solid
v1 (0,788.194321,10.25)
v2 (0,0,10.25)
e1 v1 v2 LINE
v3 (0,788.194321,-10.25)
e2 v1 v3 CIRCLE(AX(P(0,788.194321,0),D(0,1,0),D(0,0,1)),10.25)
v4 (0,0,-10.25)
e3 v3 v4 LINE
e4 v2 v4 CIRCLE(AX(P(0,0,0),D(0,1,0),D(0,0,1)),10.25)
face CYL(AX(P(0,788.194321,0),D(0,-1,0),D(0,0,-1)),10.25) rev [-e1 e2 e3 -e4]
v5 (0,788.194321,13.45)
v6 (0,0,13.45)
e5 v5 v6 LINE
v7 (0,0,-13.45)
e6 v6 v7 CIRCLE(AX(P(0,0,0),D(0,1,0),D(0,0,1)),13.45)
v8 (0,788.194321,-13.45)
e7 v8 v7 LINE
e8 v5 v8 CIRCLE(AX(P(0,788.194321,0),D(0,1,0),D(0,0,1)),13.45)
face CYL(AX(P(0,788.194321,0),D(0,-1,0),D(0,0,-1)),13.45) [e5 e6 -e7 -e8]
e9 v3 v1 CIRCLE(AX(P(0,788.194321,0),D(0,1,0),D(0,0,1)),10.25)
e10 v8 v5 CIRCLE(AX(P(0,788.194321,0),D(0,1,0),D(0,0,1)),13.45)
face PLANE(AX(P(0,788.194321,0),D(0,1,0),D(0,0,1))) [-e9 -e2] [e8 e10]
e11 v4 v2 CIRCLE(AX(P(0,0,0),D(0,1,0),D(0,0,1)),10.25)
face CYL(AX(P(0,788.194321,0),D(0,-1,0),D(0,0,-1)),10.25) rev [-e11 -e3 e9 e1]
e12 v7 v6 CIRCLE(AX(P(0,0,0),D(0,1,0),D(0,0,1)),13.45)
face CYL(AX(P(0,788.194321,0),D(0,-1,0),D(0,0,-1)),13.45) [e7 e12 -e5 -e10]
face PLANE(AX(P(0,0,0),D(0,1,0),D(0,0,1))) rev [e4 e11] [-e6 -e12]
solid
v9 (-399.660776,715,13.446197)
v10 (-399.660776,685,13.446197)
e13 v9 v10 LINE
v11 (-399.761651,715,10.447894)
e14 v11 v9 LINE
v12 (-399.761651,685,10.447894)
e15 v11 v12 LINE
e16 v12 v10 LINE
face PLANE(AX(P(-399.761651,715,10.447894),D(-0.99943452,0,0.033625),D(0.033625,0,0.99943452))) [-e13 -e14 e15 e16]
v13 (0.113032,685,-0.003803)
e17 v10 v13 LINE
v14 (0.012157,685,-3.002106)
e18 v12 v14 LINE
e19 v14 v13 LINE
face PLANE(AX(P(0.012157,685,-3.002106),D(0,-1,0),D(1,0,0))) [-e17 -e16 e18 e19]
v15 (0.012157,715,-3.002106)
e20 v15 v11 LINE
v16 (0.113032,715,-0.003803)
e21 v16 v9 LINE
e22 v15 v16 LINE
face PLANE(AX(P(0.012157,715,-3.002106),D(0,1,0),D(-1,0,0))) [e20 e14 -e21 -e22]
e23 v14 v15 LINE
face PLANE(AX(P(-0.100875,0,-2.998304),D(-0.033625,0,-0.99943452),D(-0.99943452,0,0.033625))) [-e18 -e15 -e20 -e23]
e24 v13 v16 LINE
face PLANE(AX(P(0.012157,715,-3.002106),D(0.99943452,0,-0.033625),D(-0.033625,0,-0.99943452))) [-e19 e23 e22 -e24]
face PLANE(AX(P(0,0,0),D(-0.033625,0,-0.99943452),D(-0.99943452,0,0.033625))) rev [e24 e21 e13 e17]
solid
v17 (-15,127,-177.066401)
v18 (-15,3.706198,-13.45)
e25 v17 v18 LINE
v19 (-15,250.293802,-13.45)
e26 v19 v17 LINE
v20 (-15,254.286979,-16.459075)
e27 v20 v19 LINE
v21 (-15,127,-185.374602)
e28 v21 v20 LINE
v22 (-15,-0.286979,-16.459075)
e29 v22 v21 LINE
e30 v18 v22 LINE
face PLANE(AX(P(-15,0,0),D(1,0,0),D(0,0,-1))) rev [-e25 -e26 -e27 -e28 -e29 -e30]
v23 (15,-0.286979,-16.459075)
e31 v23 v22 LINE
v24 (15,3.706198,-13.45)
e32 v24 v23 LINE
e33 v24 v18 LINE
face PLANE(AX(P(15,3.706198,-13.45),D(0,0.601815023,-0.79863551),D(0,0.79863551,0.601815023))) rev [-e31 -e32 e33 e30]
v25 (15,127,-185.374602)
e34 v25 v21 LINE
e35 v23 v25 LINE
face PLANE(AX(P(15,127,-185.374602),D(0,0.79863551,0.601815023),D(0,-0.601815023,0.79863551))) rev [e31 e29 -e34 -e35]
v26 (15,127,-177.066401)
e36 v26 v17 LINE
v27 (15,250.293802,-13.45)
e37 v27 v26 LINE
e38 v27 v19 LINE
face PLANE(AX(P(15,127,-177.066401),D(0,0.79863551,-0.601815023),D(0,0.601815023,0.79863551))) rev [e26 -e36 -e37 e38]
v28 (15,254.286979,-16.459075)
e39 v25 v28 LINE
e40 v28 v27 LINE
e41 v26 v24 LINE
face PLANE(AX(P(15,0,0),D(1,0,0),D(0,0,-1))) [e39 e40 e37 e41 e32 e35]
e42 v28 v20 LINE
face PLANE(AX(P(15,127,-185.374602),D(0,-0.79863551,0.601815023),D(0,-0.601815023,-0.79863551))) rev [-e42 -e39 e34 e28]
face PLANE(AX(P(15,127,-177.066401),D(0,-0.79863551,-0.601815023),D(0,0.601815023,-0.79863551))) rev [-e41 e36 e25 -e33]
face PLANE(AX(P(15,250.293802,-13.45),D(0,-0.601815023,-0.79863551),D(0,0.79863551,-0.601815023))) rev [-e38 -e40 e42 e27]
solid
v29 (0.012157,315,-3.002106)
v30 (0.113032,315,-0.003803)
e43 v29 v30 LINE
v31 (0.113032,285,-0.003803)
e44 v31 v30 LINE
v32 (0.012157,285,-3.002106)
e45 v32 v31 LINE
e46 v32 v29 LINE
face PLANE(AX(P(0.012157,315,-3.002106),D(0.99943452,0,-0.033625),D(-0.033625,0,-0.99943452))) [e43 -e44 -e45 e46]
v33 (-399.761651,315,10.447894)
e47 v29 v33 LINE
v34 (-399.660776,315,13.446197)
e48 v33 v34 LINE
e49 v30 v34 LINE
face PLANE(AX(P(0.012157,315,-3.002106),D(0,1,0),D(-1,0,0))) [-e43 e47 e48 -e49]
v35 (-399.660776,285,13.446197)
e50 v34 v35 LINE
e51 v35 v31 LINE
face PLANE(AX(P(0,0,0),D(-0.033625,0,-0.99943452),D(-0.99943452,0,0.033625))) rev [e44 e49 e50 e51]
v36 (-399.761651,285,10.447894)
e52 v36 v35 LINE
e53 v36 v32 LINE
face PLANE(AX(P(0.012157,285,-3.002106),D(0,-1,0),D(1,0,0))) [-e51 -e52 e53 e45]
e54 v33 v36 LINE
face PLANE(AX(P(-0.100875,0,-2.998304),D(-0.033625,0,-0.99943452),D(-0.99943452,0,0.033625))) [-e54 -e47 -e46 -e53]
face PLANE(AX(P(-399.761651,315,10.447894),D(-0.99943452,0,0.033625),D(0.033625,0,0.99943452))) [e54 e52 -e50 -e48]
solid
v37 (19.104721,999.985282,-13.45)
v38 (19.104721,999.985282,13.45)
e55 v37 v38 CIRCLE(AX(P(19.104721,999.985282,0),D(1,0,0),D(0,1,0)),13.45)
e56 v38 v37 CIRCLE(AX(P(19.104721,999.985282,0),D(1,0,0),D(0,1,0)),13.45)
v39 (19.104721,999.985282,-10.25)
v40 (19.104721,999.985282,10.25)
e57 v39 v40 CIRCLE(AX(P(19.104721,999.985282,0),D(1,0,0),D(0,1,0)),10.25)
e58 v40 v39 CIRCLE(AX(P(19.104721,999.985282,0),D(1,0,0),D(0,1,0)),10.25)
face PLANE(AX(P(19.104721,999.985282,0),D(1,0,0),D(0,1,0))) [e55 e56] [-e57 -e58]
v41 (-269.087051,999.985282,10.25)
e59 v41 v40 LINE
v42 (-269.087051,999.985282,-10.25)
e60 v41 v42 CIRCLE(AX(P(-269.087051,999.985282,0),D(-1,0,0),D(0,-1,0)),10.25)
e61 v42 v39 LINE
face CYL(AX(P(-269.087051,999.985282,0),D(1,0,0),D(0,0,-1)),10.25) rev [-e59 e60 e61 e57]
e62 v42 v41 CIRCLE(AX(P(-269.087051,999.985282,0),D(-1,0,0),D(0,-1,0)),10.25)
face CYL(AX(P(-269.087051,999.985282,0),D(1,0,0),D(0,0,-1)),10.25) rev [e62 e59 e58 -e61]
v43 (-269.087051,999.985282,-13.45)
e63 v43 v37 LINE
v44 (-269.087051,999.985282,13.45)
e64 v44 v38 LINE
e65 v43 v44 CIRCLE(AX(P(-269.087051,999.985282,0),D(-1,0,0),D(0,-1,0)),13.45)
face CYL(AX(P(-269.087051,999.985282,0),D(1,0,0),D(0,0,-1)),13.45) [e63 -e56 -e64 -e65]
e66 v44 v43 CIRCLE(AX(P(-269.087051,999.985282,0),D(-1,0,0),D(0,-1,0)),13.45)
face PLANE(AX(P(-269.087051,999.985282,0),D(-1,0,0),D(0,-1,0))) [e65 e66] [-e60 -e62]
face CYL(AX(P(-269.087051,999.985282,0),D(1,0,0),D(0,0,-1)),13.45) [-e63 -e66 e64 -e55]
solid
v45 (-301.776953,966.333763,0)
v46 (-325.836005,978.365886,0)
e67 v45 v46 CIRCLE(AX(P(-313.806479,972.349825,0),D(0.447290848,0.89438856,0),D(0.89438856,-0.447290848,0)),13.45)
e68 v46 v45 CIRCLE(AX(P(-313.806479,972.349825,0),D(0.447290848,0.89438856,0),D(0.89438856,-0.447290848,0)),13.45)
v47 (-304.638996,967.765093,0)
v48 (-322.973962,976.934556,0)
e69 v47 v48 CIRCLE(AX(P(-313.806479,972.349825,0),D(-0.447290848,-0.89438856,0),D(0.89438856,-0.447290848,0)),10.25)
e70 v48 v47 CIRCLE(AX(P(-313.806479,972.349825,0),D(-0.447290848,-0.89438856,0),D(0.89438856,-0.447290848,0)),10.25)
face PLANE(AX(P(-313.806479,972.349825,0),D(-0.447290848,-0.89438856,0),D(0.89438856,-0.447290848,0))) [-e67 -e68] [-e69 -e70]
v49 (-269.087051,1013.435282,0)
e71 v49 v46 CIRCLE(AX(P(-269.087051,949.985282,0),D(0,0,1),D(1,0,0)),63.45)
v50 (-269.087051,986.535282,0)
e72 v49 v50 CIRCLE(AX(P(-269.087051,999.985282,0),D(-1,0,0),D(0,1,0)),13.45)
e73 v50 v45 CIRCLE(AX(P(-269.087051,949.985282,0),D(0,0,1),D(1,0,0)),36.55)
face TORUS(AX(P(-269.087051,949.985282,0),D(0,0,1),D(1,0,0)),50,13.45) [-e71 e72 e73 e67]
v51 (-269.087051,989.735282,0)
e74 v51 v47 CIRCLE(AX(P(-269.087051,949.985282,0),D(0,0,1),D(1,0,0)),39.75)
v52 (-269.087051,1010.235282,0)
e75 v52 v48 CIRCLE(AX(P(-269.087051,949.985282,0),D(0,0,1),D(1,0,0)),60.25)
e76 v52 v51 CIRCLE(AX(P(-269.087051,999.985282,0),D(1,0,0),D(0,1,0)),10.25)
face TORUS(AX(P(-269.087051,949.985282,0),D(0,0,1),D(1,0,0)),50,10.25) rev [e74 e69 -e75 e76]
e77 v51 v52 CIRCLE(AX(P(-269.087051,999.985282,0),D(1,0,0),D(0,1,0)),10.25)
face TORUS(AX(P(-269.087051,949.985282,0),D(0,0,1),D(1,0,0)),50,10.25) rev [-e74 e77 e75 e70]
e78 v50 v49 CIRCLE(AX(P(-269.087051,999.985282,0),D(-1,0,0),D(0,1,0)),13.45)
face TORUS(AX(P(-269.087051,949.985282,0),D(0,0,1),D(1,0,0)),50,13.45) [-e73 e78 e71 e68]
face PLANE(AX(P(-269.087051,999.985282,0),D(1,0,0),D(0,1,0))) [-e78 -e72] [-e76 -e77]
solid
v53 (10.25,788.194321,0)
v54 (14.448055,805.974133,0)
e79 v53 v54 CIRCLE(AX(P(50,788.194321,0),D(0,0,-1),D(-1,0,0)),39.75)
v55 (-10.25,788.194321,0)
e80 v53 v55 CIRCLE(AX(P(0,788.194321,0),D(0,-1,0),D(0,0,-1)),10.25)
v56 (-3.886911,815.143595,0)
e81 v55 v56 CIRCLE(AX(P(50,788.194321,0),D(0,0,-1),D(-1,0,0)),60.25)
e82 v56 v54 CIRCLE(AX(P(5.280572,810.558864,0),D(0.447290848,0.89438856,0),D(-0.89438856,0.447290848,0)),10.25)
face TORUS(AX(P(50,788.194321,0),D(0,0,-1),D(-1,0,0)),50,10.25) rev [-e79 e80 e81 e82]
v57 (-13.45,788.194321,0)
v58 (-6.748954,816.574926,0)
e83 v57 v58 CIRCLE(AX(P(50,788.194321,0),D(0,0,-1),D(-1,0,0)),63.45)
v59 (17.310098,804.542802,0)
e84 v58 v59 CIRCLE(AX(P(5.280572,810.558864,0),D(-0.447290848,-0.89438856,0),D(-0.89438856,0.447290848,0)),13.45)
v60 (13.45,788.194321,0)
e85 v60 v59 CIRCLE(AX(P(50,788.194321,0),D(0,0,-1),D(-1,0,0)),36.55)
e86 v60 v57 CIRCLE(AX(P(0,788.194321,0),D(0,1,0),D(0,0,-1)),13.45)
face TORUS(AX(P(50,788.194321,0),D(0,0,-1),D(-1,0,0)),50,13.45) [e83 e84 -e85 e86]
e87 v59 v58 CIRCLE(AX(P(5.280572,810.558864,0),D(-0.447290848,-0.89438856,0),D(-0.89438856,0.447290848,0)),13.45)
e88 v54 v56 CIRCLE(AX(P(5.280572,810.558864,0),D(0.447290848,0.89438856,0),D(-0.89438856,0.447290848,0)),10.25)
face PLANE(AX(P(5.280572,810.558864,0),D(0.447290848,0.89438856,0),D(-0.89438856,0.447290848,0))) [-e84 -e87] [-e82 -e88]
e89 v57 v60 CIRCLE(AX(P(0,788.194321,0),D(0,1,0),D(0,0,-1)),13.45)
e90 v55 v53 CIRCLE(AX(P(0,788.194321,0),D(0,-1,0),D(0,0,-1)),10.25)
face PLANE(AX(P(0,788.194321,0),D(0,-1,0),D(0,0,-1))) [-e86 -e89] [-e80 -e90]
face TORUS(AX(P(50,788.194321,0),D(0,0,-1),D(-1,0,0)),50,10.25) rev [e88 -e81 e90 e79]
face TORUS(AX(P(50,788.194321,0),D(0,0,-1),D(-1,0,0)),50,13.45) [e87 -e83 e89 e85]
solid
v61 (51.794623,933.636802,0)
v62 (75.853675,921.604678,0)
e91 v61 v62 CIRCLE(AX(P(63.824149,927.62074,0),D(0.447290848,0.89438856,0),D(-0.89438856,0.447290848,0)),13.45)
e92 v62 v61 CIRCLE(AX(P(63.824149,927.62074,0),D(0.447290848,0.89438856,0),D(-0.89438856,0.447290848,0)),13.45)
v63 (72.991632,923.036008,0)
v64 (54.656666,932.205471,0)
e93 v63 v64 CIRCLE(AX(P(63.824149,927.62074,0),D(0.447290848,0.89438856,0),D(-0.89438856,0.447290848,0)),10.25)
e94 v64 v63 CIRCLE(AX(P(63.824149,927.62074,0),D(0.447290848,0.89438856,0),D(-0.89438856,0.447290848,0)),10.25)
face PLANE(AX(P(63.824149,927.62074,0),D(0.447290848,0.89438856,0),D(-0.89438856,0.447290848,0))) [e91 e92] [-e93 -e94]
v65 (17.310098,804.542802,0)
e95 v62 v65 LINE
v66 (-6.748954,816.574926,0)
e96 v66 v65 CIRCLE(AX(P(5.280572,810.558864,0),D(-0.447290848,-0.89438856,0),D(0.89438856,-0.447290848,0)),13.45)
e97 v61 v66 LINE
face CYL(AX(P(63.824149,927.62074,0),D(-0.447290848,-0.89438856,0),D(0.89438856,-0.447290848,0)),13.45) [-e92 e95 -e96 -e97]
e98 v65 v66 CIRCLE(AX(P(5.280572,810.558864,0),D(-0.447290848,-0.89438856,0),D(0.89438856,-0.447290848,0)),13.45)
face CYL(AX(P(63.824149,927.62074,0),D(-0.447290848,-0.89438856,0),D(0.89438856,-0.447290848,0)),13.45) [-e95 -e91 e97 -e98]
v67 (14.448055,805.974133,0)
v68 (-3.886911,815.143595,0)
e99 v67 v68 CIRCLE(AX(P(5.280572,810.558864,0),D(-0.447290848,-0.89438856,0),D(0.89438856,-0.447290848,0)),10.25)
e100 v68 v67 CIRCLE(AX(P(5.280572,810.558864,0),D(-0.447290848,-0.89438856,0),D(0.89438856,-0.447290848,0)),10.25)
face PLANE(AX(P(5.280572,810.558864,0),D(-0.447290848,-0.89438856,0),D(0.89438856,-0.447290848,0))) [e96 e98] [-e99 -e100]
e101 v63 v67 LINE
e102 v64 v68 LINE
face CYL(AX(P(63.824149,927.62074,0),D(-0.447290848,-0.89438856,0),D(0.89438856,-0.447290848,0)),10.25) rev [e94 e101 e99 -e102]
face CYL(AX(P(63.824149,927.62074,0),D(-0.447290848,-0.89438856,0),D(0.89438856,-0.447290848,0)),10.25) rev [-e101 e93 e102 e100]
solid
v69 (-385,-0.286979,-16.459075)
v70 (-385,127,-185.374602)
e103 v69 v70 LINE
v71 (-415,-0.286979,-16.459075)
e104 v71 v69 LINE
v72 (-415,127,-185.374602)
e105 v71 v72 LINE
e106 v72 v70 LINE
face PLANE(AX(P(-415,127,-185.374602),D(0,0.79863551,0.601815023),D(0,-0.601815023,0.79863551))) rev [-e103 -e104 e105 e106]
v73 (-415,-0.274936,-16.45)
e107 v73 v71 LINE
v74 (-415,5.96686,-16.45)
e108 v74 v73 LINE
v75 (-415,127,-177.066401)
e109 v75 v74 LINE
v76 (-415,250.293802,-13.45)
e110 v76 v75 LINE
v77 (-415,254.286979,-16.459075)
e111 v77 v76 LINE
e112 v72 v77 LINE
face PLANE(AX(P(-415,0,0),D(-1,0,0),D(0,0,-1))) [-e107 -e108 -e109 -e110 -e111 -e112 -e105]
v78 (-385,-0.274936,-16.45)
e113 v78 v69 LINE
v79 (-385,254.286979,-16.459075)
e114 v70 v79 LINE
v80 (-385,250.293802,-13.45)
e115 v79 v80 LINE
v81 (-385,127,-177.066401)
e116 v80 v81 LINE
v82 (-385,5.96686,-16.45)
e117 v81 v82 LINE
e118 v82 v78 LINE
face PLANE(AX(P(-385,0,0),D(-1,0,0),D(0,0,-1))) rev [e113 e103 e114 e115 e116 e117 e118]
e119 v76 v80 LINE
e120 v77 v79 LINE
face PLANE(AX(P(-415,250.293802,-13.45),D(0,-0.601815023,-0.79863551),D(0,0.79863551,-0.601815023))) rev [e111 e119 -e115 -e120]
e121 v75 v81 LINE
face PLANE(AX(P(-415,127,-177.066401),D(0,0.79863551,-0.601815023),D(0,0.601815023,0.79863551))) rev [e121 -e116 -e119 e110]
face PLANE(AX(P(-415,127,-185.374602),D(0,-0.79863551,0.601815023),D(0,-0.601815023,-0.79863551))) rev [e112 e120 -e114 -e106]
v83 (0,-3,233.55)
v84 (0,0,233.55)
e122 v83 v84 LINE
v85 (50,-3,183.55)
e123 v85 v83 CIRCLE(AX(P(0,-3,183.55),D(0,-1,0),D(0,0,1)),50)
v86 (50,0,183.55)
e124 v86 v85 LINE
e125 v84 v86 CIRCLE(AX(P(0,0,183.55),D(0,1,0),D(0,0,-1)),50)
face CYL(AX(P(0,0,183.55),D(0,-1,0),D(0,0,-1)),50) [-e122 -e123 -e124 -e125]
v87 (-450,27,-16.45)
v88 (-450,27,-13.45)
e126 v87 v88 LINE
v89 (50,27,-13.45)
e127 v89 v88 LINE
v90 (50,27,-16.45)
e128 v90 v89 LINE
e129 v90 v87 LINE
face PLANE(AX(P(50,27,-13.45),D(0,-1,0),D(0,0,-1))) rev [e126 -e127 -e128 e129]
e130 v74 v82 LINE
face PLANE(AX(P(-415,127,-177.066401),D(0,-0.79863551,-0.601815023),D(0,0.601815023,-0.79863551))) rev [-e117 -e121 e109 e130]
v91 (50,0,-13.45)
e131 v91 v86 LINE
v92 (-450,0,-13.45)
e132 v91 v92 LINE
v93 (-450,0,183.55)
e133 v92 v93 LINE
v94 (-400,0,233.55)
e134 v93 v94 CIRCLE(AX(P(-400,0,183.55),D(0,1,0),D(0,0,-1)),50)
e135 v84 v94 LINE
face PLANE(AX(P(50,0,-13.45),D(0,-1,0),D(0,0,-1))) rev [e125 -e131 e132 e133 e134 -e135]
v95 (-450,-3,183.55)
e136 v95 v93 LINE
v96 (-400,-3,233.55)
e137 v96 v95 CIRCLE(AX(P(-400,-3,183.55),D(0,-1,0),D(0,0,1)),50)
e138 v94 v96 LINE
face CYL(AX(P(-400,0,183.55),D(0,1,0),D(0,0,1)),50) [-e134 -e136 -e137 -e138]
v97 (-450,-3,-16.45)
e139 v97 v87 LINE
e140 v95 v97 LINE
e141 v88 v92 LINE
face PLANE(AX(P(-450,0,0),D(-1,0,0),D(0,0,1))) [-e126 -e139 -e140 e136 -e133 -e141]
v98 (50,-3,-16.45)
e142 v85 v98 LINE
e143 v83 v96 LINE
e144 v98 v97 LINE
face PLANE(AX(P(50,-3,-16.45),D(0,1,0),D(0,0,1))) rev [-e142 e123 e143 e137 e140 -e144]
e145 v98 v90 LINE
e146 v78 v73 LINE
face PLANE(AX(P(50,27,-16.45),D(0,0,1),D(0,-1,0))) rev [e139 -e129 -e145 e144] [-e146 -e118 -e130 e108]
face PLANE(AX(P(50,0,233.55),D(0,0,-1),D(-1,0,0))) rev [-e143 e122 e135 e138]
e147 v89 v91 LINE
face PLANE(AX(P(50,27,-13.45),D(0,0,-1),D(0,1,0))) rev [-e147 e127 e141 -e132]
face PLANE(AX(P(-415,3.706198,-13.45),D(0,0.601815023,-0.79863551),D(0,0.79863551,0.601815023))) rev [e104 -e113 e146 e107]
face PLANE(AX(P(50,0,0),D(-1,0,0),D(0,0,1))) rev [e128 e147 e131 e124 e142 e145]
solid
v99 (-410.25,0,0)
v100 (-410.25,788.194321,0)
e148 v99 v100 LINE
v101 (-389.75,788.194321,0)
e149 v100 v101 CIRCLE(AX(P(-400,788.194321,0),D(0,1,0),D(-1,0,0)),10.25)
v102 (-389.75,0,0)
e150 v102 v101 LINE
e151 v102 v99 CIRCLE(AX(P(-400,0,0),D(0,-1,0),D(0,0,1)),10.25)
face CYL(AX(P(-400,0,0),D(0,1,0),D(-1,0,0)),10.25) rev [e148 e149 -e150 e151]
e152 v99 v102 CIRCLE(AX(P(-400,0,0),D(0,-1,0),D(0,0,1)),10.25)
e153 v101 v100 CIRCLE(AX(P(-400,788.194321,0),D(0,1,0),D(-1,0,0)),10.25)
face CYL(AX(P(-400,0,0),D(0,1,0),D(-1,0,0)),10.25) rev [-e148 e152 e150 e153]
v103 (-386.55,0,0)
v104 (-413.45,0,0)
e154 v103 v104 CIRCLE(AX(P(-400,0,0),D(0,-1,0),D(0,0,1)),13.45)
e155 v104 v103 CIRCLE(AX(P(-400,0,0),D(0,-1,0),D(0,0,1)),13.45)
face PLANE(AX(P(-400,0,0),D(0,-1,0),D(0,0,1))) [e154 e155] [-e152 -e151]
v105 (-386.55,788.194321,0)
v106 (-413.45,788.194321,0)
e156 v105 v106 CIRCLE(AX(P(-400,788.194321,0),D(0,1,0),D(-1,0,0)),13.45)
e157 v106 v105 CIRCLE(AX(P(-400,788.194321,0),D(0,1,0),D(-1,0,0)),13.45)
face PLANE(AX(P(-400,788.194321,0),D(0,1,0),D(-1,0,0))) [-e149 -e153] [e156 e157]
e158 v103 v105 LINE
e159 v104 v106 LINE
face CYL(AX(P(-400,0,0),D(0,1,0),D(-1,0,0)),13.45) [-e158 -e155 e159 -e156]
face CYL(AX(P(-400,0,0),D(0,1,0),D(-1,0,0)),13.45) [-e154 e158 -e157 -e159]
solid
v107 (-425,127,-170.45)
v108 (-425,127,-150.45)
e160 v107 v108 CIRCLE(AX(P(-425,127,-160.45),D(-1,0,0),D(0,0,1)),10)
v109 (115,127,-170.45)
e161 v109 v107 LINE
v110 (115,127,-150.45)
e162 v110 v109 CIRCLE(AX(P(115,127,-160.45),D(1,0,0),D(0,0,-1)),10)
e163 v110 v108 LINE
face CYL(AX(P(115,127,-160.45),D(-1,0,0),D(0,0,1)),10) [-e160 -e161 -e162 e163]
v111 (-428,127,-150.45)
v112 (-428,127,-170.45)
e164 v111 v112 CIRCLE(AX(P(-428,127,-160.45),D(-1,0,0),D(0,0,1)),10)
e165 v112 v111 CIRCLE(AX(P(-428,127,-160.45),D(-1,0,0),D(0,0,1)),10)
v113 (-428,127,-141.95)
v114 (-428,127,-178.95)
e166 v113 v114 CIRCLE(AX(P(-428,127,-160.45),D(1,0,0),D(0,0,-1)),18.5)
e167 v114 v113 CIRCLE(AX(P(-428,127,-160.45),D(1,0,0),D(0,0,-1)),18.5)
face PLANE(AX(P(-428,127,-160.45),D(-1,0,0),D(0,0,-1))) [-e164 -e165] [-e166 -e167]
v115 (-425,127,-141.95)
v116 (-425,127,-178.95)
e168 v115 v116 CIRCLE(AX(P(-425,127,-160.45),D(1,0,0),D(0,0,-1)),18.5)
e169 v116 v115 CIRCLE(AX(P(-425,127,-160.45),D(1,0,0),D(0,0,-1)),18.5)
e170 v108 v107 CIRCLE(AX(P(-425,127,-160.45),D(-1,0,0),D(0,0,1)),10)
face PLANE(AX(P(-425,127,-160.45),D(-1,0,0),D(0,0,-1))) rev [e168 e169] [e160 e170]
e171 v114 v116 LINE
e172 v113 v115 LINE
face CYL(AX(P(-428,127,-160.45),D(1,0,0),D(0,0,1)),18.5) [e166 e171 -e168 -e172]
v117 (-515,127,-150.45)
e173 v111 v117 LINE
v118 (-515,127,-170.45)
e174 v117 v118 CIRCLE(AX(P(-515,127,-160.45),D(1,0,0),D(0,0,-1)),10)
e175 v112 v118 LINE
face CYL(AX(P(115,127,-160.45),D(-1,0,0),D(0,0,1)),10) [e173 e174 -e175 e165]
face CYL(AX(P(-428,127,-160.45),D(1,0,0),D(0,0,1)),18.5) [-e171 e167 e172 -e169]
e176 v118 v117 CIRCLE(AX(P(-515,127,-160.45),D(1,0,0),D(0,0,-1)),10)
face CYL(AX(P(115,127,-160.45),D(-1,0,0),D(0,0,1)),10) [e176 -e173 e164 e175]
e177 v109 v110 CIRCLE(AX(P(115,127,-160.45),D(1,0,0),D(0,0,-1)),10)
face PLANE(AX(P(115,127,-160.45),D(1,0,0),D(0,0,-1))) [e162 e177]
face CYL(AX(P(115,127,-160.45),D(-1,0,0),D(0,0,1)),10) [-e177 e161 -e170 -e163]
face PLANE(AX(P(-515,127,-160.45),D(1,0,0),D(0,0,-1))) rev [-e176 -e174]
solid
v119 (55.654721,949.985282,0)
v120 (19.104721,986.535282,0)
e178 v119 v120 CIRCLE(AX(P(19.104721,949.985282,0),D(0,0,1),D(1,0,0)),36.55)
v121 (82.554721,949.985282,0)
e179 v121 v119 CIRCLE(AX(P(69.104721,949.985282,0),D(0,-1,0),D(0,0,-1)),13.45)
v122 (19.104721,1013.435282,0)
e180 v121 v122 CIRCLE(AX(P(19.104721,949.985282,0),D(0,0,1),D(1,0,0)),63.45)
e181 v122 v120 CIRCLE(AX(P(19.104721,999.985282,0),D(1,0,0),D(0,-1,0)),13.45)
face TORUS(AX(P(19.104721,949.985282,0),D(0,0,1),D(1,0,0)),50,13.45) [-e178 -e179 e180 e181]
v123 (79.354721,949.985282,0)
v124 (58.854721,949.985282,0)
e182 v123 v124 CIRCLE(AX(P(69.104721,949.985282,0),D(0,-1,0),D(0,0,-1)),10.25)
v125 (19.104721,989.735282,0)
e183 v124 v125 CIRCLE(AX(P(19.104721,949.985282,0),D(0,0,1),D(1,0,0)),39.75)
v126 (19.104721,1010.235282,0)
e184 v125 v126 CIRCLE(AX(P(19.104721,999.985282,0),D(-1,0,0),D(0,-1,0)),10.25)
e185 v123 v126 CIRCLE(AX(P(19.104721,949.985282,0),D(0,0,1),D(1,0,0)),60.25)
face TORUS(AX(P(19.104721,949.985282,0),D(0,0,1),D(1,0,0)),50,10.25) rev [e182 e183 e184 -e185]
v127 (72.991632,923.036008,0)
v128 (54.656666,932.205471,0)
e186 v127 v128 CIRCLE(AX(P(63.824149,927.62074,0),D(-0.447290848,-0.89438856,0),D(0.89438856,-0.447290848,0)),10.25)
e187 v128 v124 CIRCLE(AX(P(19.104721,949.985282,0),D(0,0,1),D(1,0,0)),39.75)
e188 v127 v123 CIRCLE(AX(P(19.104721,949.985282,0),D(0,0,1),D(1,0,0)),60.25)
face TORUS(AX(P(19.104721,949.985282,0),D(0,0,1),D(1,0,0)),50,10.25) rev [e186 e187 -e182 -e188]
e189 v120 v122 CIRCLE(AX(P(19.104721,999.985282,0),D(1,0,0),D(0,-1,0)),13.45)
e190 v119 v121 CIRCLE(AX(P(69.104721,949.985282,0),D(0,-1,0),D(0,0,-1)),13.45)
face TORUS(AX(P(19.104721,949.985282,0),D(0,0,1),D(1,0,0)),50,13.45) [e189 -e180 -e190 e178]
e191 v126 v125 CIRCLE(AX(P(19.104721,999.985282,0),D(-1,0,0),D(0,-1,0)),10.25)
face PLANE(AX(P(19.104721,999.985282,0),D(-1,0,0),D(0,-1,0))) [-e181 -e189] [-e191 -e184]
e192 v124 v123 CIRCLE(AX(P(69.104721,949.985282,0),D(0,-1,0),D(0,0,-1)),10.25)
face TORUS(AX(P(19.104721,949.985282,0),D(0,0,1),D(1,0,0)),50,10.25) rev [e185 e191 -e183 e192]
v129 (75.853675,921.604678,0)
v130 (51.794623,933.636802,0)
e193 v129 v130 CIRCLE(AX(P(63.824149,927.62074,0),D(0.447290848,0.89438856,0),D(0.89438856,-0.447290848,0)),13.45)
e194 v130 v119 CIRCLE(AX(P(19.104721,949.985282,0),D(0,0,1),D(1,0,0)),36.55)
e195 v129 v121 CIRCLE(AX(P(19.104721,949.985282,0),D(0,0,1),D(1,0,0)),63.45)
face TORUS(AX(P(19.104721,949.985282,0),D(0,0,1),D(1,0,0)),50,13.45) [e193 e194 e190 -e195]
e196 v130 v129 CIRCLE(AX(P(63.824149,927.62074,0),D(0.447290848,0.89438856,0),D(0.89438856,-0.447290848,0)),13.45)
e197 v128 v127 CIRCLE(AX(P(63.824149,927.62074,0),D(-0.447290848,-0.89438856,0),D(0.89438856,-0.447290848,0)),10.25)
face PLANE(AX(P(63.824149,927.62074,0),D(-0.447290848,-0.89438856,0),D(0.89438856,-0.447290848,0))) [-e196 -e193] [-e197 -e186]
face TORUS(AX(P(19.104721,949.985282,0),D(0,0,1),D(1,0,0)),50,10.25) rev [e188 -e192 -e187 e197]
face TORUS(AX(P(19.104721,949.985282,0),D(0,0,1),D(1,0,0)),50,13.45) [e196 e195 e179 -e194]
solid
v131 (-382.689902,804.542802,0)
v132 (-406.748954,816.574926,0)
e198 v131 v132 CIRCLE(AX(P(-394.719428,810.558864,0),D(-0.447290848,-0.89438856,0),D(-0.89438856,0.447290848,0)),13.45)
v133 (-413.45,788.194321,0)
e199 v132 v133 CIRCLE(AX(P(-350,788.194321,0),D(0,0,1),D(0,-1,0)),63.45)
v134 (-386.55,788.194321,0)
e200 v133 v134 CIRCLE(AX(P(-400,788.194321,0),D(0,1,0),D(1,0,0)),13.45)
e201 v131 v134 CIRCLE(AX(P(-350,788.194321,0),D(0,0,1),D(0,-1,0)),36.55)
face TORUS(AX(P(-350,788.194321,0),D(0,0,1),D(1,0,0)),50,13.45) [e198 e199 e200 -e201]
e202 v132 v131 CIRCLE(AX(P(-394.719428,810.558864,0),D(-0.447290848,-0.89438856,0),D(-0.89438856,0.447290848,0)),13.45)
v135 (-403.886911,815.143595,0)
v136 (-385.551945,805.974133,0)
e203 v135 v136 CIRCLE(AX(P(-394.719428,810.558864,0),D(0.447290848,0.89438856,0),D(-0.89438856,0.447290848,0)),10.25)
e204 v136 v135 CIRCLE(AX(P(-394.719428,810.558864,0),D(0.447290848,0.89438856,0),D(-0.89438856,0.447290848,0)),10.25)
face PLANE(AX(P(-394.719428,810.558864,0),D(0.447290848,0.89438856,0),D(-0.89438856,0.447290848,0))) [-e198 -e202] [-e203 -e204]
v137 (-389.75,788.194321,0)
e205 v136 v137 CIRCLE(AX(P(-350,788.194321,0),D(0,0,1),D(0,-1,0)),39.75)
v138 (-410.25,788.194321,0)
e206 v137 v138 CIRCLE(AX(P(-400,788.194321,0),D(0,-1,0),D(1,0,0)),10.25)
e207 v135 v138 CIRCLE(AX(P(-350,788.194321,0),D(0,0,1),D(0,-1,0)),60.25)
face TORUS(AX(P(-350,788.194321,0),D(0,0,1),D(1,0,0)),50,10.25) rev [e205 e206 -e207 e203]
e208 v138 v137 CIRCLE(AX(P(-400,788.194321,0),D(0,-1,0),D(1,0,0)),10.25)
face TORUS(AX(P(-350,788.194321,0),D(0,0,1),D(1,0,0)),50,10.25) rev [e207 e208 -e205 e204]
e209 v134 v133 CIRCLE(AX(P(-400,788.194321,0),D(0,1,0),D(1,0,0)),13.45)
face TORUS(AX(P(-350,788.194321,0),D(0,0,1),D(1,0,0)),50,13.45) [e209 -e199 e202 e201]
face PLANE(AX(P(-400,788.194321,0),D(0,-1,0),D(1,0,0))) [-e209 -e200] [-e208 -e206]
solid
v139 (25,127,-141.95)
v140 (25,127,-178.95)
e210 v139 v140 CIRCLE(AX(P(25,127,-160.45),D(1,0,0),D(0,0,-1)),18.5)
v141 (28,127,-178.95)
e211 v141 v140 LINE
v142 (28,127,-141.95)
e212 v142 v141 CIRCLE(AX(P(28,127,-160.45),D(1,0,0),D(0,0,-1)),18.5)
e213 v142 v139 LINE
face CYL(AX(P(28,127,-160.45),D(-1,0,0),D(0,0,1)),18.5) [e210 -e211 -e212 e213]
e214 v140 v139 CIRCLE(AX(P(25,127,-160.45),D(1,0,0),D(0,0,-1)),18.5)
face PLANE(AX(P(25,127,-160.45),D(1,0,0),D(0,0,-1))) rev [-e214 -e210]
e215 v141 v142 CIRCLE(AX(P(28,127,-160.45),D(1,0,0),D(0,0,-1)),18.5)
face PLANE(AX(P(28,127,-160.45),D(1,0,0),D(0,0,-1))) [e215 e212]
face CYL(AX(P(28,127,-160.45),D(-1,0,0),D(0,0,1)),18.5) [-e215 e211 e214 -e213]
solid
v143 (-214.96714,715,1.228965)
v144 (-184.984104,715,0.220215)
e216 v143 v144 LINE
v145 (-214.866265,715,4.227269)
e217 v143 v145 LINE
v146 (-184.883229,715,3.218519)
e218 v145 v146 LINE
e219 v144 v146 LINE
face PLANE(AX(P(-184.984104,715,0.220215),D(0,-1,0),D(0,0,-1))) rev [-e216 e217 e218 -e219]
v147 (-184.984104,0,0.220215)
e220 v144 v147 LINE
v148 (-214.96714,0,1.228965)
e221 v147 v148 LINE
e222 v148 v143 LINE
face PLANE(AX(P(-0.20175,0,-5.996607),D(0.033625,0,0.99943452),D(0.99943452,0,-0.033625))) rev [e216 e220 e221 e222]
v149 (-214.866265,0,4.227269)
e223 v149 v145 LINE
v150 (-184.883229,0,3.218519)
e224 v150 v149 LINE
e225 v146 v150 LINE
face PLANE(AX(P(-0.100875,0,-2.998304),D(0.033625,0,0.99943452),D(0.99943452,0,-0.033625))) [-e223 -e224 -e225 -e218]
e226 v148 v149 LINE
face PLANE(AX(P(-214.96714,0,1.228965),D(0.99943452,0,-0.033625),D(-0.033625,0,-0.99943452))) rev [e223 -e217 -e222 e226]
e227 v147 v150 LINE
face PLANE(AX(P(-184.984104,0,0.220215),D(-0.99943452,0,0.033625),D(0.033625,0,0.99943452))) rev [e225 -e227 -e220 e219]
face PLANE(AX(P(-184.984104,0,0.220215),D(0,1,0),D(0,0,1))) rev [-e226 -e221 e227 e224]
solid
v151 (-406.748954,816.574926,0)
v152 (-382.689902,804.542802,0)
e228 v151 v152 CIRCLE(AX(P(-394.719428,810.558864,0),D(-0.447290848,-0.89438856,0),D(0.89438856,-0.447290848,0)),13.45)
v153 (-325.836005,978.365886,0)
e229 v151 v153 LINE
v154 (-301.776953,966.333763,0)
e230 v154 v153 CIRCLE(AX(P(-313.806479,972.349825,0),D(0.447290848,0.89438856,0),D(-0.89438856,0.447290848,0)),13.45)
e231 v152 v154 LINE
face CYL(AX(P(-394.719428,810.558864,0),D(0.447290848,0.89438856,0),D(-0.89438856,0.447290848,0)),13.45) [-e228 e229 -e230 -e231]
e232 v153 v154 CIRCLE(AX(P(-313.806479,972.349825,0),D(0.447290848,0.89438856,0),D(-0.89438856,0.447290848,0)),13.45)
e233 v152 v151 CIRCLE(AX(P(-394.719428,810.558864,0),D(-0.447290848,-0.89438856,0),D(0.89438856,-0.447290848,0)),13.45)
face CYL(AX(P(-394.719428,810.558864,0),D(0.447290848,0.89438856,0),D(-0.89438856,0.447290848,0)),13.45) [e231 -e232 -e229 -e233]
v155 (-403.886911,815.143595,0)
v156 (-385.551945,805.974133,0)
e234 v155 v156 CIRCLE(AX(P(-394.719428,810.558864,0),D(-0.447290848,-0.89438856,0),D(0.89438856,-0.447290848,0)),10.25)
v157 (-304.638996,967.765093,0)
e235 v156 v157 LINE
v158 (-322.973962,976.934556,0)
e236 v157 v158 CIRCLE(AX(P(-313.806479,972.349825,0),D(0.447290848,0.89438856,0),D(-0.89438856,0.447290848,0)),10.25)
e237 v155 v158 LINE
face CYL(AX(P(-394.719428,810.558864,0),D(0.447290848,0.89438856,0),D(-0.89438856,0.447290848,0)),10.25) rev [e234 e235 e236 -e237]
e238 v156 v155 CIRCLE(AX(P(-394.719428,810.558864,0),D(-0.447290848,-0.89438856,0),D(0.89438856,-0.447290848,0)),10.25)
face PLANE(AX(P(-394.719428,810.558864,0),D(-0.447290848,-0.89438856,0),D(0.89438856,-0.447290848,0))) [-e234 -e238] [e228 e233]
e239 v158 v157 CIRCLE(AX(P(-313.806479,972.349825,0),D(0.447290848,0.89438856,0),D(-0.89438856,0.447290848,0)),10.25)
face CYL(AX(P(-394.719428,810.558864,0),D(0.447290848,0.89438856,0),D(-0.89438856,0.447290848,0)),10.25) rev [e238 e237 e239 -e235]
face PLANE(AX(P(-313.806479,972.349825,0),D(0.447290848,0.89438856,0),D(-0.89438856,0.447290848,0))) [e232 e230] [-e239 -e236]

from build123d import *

# Parameters (mm, degrees)
SKETCH1_R                       = 13.45
SKETCH1_R_2                     = 10.25
PIPE_26_9_X_3_2_1_DEPTH         = 788.194321435
SKETCH1_ON_SEGMENT_2_R          = 13.45
SKETCH1_ON_SEGMENT_2_R_2        = 10.25
PIPE_26_9_X_3_2_1_2_ANGLE       = 26.57
SKETCH1_ON_SEGMENT_3_R          = 13.45
SKETCH1_ON_SEGMENT_3_R_2        = 10.25
PIPE_26_9_X_3_2_1_3_DEPTH       = 130.884808917
SKETCH1_ON_SEGMENT_4_R          = 13.45
SKETCH1_ON_SEGMENT_4_R_2        = 10.25
PIPE_26_9_X_3_2_1_4_ANGLE       = 116.57
SKETCH1_ON_SEGMENT_5_R          = 13.45
SKETCH1_ON_SEGMENT_5_R_2        = 10.25
PIPE_26_9_X_3_2_1_5_DEPTH       = 288.191772088
SKETCH1_ON_SEGMENT_6_R          = 13.45
SKETCH1_ON_SEGMENT_6_R_2        = 10.25
PIPE_26_9_X_3_2_1_6_ANGLE       = 63.43
SKETCH1_ON_SEGMENT_7_R          = 13.45
SKETCH1_ON_SEGMENT_7_R_2        = 10.25
PIPE_26_9_X_3_2_1_7_DEPTH       = 180.89560604
SKETCH1_ON_SEGMENT_8_R          = 13.45
SKETCH1_ON_SEGMENT_8_R_2        = 10.25
PIPE_26_9_X_3_2_1_8_ANGLE       = 26.57
SKETCH1_ON_SEGMENT_9_R          = 13.45
SKETCH1_ON_SEGMENT_9_R_2        = 10.25
PIPE_26_9_X_3_2_1_9_DEPTH       = 788.194321435
CROSS_BARS_SKETCH_W             = 400
CROSS_BARS_SKETCH_H             = 30
CROSS_BARS_30X3_DEPTH           = 3
CROSS_BARS_30X3_2_DEPTH         = 3
CENTRE_UPRIGHT_SKETCH_W         = 30
CENTRE_UPRIGHT_SKETCH_H         = 715
CENTRE_UPRIGHT_BAR_30X3_DEPTH   = 3
NOSE_PLATE_DEPTH                = 250
NOSE_PLATE_CORNER_FILLETS_R50_R = 50
AXLE_SKETCH_20_R                = 10
AXLE_20_DEPTH                   = 315
AXLE_BRACKET_DEPTH              = 15
WHEEL_COLLAR_SKETCH_37_R        = 18.5
WHEEL_COLLAR_37_DEPTH           = 3


with BuildPart() as part:
    # Sketch1 → Pipe 26.9 X 3.2(1) (new body)
    with BuildSketch(Plane(origin=(0, 0, 0), x_dir=(1, 0, 0), z_dir=(0, 1, 0))):
        Circle(SKETCH1_R)
        Circle(SKETCH1_R_2, mode=Mode.SUBTRACT)
    extrude(amount=PIPE_26_9_X_3_2_1_DEPTH)


with BuildPart() as body_2:
    # Sketch1 on segment 2 (carried to the start of arc 2) → Pipe 26.9 X 3.2_1 2 (revolve)
    with BuildSketch(Plane(origin=(0, 788.194321435, 0), x_dir=(1, 0, 0), z_dir=(0, 1, 0))):
        Circle(SKETCH1_ON_SEGMENT_2_R)
        Circle(SKETCH1_ON_SEGMENT_2_R_2, mode=Mode.SUBTRACT)
    revolve(axis=Axis((50, 788.194321435, 0), (0, 0, -1)), revolution_arc=PIPE_26_9_X_3_2_1_2_ANGLE)


with BuildPart() as body_3:
    # Sketch1 on segment 3 (carried to segment 3) → Pipe 26.9 X 3.2_1 3 (new body)
    with BuildSketch(Plane(origin=(5.280571981, 810.558863856, 0), x_dir=(0.89438856, -0.447290848, 0), z_dir=(0.447290848, 0.89438856, 0))):
        Circle(SKETCH1_ON_SEGMENT_3_R)
        Circle(SKETCH1_ON_SEGMENT_3_R_2, mode=Mode.SUBTRACT)
    extrude(amount=PIPE_26_9_X_3_2_1_3_DEPTH)


with BuildPart() as body_4:
    # Sketch1 on segment 4 (carried to the start of arc 4) → Pipe 26.9 X 3.2_1 4 (revolve)
    with BuildSketch(Plane(origin=(63.824149207, 927.620739678, 0), x_dir=(0.89438856, -0.447290848, 0), z_dir=(0.447290848, 0.89438856, 0))):
        Circle(SKETCH1_ON_SEGMENT_4_R)
        Circle(SKETCH1_ON_SEGMENT_4_R_2, mode=Mode.SUBTRACT)
    revolve(axis=Axis((19.104721189, 949.985282099, 0), (0, 0, 1)), revolution_arc=PIPE_26_9_X_3_2_1_4_ANGLE)


with BuildPart() as body_5:
    # Sketch1 on segment 5 (carried to segment 5) → Pipe 26.9 X 3.2_1 5 (new body)
    with BuildSketch(Plane(origin=(19.104721189, 999.985282099, 0), x_dir=(0, 1, 0), z_dir=(-1, 0, 0))):
        Circle(SKETCH1_ON_SEGMENT_5_R)
        Circle(SKETCH1_ON_SEGMENT_5_R_2, mode=Mode.SUBTRACT)
    extrude(amount=PIPE_26_9_X_3_2_1_5_DEPTH)


with BuildPart() as body_6:
    # Sketch1 on segment 6 (carried to the start of arc 6) → Pipe 26.9 X 3.2_1 6 (revolve)
    with BuildSketch(Plane(origin=(-269.087050899, 999.985282099, 0), x_dir=(0, 1, 0), z_dir=(-1, 0, 0))):
        Circle(SKETCH1_ON_SEGMENT_6_R)
        Circle(SKETCH1_ON_SEGMENT_6_R_2, mode=Mode.SUBTRACT)
    revolve(axis=Axis((-269.087050899, 949.985282099, 0), (0, 0, 1)), revolution_arc=PIPE_26_9_X_3_2_1_6_ANGLE)


with BuildPart() as body_7:
    # Sketch1 on segment 7 (carried to segment 7) → Pipe 26.9 X 3.2_1 7 (new body)
    with BuildSketch(Plane(origin=(-313.806478917, 972.34982452, 0), x_dir=(-0.89438856, 0.447290848, 0), z_dir=(-0.447290848, -0.89438856, 0))):
        Circle(SKETCH1_ON_SEGMENT_7_R)
        Circle(SKETCH1_ON_SEGMENT_7_R_2, mode=Mode.SUBTRACT)
    extrude(amount=PIPE_26_9_X_3_2_1_7_DEPTH)


with BuildPart() as body_8:
    # Sketch1 on segment 8 (carried to the start of arc 8) → Pipe 26.9 X 3.2_1 8 (revolve)
    with BuildSketch(Plane(origin=(-394.719428019, 810.558863856, 0), x_dir=(-0.89438856, 0.447290848, 0), z_dir=(-0.447290848, -0.89438856, 0))):
        Circle(SKETCH1_ON_SEGMENT_8_R)
        Circle(SKETCH1_ON_SEGMENT_8_R_2, mode=Mode.SUBTRACT)
    revolve(axis=Axis((-350, 788.194321435, 0), (0, 0, 1)), revolution_arc=PIPE_26_9_X_3_2_1_8_ANGLE)


with BuildPart() as body_9:
    # Sketch1 on segment 9 (carried to segment 9) → Pipe 26.9 X 3.2_1 9 (new body)
    with BuildSketch(Plane(origin=(-400, 0, 0), x_dir=(1, 0, 0), z_dir=(0, 1, 0))):
        Circle(SKETCH1_ON_SEGMENT_9_R)
        Circle(SKETCH1_ON_SEGMENT_9_R_2, mode=Mode.SUBTRACT)
    extrude(amount=PIPE_26_9_X_3_2_1_9_DEPTH)


with BuildPart() as body_10:
    # Cross Bars Sketch → Cross Bars 30x3 (new body)
    with BuildSketch(Plane(origin=(0, 0, 0), x_dir=(0.9994345198035738, 0, -0.03362500000000007), z_dir=(0.03362500000000007, 0, 0.9994345198035738))):
        with Locations((-199.886903961, 700)):
            Rectangle(CROSS_BARS_SKETCH_W, CROSS_BARS_SKETCH_H)
    extrude(amount=-CROSS_BARS_30X3_DEPTH)


with BuildPart() as body_11:
    # Cross Bars Sketch → Cross Bars 30x3 2 (new body)
    with BuildSketch(Plane(origin=(0, 0, 0), x_dir=(0.9994345198035738, 0, -0.03362500000000007), z_dir=(0.03362500000000007, 0, 0.9994345198035738))):
        with Locations((-199.886903961, 300)):
            Rectangle(CROSS_BARS_SKETCH_W, CROSS_BARS_SKETCH_H)
    extrude(amount=-CROSS_BARS_30X3_2_DEPTH)


with BuildPart() as body_12:
    # Centre Upright Sketch → Centre Upright Bar 30x3 (new body)
    with BuildSketch(Plane(origin=(-0.100875, 0, -2.998303559), x_dir=(-0.9994345198035738, 0, 0.033625000000000065), z_dir=(-0.033625000000000065, 0, -0.9994345198035738))):
        with Locations((199.886903961, 357.5)):
            Rectangle(CENTRE_UPRIGHT_SKETCH_W, CENTRE_UPRIGHT_SKETCH_H)
    extrude(amount=CENTRE_UPRIGHT_BAR_30X3_DEPTH)


with BuildPart() as body_13:
    # Nose Plate Profile → Nose Plate (new, symmetric)
    with BuildSketch(Plane(origin=(-200, 0, 0), x_dir=(0, 0, -1), z_dir=(1, 0, 0))):
        Polygon((16.45, 27), (16.45, -3), (-233.55, -3), (-233.55, 0), (13.45, 0), (13.45, 27), align=None)
    extrude(amount=NOSE_PLATE_DEPTH, both=True)

    # Nose Plate Corner Fillets R50
    nose_plate_corner_fillets_r50_edges = [body_13.edges().sort_by_distance(p)[0] for p in [
        (50, -1.5, 233.55),
        (-450, -1.5, 233.55),
    ]]
    fillet(nose_plate_corner_fillets_r50_edges, radius=NOSE_PLATE_CORNER_FILLETS_R50_R)


with BuildPart() as body_14:
    # Axle Sketch Ø20 → Axle Ø20 (new, symmetric)
    with BuildSketch(Plane(origin=(-200, 0, 0), x_dir=(0, 0, -1), z_dir=(1, 0, 0))):
        with Locations((160.45, 127)):
            Circle(AXLE_SKETCH_20_R)
    extrude(amount=AXLE_20_DEPTH, both=True)


with BuildPart() as body_15:
    # Axle Bracket Profile → Axle Bracket (new, symmetric)
    with BuildSketch(Plane(origin=(0, 0, 0), x_dir=(0, 0, -1), z_dir=(1, 0, 0))):
        Polygon((177.066401411, 127), (13.45, 250.293801947), (16.459075116, 254.286979497), (185.374602117, 127), (16.459075116, -0.286979497), (13.45, 3.706198053), align=None)
    axle_bracket = extrude(amount=AXLE_BRACKET_DEPTH, both=True)


with BuildPart() as body_13_1:
    add(body_13.part)

    # Axle Bracket Mirror: Axle Bracket across plane
    add(axle_bracket.mirror(Plane(origin=(-200, 0, 0), x_dir=(0, 0, 1), z_dir=(1, 0, 0))))


with BuildPart() as body_16:
    # Wheel Collar Sketch Ø37 → Wheel Collar Ø37 (new body)
    with BuildSketch(Plane(origin=(25, 0, 0), x_dir=(0, 0, -1), z_dir=(1, 0, 0))):
        with Locations((160.45, 127)):
            Circle(WHEEL_COLLAR_SKETCH_37_R)
    wheel_collar_37 = extrude(amount=WHEEL_COLLAR_37_DEPTH)


with BuildPart() as body_14_1:
    add(body_14.part)

    # Wheel Collar Mirror: Wheel Collar Ø37 across plane
    add(wheel_collar_37.mirror(Plane(origin=(-200, 0, 0), x_dir=(0, 0, 1), z_dir=(1, 0, 0))))


solid = Compound([part.part, body_2.part, body_3.part, body_4.part, body_5.part, body_6.part, body_7.part, body_8.part, body_9.part, body_10.part, body_11.part, body_12.part, body_15.part, body_13_1.part, body_16.part, body_14_1.part])
